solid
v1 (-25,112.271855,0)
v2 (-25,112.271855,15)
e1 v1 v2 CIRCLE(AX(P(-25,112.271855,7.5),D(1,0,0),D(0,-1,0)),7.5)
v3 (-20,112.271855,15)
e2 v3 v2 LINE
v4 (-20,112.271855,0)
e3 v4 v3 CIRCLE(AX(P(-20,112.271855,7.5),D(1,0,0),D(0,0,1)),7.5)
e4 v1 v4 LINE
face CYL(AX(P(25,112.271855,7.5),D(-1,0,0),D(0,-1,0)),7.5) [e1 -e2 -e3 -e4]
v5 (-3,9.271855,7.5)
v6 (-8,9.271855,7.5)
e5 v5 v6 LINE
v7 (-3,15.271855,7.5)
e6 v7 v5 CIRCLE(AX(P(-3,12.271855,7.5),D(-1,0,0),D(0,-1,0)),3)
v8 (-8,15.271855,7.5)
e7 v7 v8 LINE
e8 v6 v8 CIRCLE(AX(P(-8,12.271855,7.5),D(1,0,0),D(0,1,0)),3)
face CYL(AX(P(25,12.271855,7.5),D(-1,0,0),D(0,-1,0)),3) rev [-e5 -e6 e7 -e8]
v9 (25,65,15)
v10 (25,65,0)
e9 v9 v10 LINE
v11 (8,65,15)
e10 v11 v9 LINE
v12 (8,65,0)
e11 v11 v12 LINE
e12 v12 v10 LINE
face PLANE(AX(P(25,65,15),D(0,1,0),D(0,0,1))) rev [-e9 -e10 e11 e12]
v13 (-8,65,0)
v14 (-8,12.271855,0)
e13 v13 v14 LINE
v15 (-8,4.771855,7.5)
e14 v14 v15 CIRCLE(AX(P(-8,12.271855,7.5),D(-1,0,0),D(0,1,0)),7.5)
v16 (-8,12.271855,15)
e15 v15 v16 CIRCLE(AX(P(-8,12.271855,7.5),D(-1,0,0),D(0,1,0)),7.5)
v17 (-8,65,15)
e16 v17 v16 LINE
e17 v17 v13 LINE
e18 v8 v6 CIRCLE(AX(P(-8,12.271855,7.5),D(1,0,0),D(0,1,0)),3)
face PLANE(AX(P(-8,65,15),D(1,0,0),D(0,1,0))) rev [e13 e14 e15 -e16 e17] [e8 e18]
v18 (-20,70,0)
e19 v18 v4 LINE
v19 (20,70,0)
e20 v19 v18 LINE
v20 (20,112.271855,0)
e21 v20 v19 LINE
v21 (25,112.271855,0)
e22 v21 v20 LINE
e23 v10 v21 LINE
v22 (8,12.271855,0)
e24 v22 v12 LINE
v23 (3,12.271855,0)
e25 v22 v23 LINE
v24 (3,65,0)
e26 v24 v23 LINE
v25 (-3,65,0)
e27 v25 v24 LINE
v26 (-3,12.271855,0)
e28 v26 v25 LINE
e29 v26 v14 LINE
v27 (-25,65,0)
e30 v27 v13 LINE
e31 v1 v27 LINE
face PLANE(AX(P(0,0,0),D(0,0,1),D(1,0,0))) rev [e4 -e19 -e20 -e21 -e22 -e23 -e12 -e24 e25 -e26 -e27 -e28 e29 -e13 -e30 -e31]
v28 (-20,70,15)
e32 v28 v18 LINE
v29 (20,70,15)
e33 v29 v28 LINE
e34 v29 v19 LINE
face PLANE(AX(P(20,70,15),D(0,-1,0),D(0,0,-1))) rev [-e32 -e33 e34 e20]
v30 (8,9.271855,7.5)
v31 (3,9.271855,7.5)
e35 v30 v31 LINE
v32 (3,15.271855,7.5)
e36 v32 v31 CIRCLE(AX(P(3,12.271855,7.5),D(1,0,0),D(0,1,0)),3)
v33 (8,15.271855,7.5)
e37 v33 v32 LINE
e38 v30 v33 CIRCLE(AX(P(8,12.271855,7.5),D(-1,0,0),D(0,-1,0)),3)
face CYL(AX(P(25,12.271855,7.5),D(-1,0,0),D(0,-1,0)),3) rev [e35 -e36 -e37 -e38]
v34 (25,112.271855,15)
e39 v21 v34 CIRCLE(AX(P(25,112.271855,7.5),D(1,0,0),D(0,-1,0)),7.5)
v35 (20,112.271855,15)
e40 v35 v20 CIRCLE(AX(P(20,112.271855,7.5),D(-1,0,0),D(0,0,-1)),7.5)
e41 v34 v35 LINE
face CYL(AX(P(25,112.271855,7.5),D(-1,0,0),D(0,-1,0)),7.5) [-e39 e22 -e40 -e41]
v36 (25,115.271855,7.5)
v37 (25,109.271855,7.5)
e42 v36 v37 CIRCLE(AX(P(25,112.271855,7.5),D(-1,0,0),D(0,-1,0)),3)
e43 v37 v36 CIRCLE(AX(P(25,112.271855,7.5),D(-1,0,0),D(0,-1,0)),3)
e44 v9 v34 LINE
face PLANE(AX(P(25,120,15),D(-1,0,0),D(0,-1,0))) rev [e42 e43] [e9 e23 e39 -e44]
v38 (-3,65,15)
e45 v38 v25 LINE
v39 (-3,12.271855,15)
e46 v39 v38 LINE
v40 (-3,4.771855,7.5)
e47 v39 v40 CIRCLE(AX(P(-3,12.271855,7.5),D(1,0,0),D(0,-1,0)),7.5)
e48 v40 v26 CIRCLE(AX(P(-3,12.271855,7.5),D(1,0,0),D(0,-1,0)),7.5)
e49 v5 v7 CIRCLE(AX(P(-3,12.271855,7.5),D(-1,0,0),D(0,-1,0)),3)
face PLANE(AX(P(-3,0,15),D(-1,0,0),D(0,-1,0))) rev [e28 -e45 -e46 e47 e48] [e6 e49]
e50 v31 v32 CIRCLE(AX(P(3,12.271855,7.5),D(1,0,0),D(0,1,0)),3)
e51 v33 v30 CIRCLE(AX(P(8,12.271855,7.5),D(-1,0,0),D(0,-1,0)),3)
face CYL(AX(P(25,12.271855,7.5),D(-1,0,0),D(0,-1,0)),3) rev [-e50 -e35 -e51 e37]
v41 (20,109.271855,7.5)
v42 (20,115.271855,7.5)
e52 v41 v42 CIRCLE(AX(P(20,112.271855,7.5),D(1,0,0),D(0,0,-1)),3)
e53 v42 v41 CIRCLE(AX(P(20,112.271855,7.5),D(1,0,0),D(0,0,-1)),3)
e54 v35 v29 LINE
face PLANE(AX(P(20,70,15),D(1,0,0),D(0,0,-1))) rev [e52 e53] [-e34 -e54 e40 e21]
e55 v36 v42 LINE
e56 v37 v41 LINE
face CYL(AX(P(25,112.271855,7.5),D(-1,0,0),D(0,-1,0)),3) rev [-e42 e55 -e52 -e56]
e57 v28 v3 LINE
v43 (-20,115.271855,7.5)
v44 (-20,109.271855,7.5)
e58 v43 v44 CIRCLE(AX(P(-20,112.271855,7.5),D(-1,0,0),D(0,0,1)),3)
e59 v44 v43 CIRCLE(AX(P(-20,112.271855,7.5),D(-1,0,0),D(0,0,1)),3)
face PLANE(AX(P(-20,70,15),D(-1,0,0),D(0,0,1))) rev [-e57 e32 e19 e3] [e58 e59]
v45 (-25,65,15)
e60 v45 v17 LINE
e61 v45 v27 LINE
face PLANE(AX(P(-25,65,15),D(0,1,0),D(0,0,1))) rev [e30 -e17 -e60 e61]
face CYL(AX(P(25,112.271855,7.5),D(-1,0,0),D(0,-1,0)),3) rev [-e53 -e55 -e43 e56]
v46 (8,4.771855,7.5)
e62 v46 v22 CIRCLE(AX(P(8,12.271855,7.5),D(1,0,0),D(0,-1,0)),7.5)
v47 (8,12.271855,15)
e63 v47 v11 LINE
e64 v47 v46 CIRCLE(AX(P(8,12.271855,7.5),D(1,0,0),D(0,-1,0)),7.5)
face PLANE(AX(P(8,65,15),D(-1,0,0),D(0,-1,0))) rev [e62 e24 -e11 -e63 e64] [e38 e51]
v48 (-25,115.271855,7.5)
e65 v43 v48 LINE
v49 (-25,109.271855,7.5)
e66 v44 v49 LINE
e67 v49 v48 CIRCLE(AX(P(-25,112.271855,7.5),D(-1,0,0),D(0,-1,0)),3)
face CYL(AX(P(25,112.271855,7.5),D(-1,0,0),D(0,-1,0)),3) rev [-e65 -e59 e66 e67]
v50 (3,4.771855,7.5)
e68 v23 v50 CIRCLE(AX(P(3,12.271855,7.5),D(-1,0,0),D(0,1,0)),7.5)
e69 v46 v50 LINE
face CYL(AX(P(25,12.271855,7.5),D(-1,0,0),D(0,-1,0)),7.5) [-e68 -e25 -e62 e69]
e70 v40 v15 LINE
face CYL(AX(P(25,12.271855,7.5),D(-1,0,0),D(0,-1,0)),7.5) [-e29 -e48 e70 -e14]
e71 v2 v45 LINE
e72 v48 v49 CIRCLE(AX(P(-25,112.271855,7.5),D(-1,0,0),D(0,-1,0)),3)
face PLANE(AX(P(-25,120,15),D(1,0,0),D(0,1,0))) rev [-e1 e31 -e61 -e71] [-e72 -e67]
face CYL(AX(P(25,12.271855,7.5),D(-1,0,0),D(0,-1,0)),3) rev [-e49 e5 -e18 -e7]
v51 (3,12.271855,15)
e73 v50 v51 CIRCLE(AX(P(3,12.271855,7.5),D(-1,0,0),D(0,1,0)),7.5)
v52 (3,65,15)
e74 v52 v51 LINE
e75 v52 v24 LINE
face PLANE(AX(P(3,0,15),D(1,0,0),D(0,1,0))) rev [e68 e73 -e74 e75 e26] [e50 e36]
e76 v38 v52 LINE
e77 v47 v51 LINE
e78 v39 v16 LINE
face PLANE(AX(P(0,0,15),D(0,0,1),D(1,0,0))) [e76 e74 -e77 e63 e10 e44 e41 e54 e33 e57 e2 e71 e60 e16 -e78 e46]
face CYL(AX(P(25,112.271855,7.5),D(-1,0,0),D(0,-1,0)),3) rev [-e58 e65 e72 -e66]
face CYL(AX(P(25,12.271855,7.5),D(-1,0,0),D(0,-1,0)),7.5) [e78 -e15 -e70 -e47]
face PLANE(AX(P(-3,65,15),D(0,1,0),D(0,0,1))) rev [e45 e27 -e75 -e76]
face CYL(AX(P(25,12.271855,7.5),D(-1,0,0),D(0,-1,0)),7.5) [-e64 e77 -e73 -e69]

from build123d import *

# Parameters (mm, degrees)
BOSS_EXTRUDE1_DEPTH = 15
SKETCH2_R           = 3
CUT_EXTRUDE1_DEPTH  = 131.862523283


with BuildPart() as part:
    # Sketch1 → Boss-Extrude1 (new body)
    with BuildSketch(Plane.XY):
        Polygon((-3, 0), (-3, 65), (3, 65), (3, 0), (8, 0), (8, 65), (25, 65), (25, 120), (20, 120), (20, 70), (-20, 70), (-20, 120), (-25, 120), (-25, 65), (-8, 65), (-8, 0), align=None)
    extrude(amount=BOSS_EXTRUDE1_DEPTH)

    # Sketch2 → Cut-Extrude1 (cut, through all)
    with BuildSketch(Plane.ZY.offset(25)):
        with Locations(Location((7.5, 112.271855303, 0), (0, 0, 270))):
            Circle(SKETCH2_R)
        with Locations(Location((7.5, 12.271855303, 0), (0, 0, 270))):
            Circle(SKETCH2_R)
        with BuildLine():
            Line((0, 112.271855303), (-22.426817963, 115.88465347))
            Line((-22.426817963, 115.88465347), (0, 149.126440397))
            Line((0, 149.126440397), (35.619754134, 129.721336353))
            Line((35.619754134, 129.721336353), (15, 112.271855303))
            ThreePointArc((15, 112.271855303), (7.5, 119.771855303), (0, 112.271855303))
        make_face()
        with BuildLine():
            Line((0, 12.271855303), (-15.301630232, 4.771855303))
            Line((-15.301630232, 4.771855303), (-3.280552195, -11.427643596))
            Line((-3.280552195, -11.427643596), (32.469088575, -8.187179082))
            Line((32.469088575, -8.187179082), (24.8383173, 8.521855303))
            Line((24.8383173, 8.521855303), (15, 12.271855303))
            ThreePointArc((15, 12.271855303), (7.5, 4.771855303), (0, 12.271855303))
        make_face()
    extrude(amount=-CUT_EXTRUDE1_DEPTH, mode=Mode.SUBTRACT)


solid = part.part
